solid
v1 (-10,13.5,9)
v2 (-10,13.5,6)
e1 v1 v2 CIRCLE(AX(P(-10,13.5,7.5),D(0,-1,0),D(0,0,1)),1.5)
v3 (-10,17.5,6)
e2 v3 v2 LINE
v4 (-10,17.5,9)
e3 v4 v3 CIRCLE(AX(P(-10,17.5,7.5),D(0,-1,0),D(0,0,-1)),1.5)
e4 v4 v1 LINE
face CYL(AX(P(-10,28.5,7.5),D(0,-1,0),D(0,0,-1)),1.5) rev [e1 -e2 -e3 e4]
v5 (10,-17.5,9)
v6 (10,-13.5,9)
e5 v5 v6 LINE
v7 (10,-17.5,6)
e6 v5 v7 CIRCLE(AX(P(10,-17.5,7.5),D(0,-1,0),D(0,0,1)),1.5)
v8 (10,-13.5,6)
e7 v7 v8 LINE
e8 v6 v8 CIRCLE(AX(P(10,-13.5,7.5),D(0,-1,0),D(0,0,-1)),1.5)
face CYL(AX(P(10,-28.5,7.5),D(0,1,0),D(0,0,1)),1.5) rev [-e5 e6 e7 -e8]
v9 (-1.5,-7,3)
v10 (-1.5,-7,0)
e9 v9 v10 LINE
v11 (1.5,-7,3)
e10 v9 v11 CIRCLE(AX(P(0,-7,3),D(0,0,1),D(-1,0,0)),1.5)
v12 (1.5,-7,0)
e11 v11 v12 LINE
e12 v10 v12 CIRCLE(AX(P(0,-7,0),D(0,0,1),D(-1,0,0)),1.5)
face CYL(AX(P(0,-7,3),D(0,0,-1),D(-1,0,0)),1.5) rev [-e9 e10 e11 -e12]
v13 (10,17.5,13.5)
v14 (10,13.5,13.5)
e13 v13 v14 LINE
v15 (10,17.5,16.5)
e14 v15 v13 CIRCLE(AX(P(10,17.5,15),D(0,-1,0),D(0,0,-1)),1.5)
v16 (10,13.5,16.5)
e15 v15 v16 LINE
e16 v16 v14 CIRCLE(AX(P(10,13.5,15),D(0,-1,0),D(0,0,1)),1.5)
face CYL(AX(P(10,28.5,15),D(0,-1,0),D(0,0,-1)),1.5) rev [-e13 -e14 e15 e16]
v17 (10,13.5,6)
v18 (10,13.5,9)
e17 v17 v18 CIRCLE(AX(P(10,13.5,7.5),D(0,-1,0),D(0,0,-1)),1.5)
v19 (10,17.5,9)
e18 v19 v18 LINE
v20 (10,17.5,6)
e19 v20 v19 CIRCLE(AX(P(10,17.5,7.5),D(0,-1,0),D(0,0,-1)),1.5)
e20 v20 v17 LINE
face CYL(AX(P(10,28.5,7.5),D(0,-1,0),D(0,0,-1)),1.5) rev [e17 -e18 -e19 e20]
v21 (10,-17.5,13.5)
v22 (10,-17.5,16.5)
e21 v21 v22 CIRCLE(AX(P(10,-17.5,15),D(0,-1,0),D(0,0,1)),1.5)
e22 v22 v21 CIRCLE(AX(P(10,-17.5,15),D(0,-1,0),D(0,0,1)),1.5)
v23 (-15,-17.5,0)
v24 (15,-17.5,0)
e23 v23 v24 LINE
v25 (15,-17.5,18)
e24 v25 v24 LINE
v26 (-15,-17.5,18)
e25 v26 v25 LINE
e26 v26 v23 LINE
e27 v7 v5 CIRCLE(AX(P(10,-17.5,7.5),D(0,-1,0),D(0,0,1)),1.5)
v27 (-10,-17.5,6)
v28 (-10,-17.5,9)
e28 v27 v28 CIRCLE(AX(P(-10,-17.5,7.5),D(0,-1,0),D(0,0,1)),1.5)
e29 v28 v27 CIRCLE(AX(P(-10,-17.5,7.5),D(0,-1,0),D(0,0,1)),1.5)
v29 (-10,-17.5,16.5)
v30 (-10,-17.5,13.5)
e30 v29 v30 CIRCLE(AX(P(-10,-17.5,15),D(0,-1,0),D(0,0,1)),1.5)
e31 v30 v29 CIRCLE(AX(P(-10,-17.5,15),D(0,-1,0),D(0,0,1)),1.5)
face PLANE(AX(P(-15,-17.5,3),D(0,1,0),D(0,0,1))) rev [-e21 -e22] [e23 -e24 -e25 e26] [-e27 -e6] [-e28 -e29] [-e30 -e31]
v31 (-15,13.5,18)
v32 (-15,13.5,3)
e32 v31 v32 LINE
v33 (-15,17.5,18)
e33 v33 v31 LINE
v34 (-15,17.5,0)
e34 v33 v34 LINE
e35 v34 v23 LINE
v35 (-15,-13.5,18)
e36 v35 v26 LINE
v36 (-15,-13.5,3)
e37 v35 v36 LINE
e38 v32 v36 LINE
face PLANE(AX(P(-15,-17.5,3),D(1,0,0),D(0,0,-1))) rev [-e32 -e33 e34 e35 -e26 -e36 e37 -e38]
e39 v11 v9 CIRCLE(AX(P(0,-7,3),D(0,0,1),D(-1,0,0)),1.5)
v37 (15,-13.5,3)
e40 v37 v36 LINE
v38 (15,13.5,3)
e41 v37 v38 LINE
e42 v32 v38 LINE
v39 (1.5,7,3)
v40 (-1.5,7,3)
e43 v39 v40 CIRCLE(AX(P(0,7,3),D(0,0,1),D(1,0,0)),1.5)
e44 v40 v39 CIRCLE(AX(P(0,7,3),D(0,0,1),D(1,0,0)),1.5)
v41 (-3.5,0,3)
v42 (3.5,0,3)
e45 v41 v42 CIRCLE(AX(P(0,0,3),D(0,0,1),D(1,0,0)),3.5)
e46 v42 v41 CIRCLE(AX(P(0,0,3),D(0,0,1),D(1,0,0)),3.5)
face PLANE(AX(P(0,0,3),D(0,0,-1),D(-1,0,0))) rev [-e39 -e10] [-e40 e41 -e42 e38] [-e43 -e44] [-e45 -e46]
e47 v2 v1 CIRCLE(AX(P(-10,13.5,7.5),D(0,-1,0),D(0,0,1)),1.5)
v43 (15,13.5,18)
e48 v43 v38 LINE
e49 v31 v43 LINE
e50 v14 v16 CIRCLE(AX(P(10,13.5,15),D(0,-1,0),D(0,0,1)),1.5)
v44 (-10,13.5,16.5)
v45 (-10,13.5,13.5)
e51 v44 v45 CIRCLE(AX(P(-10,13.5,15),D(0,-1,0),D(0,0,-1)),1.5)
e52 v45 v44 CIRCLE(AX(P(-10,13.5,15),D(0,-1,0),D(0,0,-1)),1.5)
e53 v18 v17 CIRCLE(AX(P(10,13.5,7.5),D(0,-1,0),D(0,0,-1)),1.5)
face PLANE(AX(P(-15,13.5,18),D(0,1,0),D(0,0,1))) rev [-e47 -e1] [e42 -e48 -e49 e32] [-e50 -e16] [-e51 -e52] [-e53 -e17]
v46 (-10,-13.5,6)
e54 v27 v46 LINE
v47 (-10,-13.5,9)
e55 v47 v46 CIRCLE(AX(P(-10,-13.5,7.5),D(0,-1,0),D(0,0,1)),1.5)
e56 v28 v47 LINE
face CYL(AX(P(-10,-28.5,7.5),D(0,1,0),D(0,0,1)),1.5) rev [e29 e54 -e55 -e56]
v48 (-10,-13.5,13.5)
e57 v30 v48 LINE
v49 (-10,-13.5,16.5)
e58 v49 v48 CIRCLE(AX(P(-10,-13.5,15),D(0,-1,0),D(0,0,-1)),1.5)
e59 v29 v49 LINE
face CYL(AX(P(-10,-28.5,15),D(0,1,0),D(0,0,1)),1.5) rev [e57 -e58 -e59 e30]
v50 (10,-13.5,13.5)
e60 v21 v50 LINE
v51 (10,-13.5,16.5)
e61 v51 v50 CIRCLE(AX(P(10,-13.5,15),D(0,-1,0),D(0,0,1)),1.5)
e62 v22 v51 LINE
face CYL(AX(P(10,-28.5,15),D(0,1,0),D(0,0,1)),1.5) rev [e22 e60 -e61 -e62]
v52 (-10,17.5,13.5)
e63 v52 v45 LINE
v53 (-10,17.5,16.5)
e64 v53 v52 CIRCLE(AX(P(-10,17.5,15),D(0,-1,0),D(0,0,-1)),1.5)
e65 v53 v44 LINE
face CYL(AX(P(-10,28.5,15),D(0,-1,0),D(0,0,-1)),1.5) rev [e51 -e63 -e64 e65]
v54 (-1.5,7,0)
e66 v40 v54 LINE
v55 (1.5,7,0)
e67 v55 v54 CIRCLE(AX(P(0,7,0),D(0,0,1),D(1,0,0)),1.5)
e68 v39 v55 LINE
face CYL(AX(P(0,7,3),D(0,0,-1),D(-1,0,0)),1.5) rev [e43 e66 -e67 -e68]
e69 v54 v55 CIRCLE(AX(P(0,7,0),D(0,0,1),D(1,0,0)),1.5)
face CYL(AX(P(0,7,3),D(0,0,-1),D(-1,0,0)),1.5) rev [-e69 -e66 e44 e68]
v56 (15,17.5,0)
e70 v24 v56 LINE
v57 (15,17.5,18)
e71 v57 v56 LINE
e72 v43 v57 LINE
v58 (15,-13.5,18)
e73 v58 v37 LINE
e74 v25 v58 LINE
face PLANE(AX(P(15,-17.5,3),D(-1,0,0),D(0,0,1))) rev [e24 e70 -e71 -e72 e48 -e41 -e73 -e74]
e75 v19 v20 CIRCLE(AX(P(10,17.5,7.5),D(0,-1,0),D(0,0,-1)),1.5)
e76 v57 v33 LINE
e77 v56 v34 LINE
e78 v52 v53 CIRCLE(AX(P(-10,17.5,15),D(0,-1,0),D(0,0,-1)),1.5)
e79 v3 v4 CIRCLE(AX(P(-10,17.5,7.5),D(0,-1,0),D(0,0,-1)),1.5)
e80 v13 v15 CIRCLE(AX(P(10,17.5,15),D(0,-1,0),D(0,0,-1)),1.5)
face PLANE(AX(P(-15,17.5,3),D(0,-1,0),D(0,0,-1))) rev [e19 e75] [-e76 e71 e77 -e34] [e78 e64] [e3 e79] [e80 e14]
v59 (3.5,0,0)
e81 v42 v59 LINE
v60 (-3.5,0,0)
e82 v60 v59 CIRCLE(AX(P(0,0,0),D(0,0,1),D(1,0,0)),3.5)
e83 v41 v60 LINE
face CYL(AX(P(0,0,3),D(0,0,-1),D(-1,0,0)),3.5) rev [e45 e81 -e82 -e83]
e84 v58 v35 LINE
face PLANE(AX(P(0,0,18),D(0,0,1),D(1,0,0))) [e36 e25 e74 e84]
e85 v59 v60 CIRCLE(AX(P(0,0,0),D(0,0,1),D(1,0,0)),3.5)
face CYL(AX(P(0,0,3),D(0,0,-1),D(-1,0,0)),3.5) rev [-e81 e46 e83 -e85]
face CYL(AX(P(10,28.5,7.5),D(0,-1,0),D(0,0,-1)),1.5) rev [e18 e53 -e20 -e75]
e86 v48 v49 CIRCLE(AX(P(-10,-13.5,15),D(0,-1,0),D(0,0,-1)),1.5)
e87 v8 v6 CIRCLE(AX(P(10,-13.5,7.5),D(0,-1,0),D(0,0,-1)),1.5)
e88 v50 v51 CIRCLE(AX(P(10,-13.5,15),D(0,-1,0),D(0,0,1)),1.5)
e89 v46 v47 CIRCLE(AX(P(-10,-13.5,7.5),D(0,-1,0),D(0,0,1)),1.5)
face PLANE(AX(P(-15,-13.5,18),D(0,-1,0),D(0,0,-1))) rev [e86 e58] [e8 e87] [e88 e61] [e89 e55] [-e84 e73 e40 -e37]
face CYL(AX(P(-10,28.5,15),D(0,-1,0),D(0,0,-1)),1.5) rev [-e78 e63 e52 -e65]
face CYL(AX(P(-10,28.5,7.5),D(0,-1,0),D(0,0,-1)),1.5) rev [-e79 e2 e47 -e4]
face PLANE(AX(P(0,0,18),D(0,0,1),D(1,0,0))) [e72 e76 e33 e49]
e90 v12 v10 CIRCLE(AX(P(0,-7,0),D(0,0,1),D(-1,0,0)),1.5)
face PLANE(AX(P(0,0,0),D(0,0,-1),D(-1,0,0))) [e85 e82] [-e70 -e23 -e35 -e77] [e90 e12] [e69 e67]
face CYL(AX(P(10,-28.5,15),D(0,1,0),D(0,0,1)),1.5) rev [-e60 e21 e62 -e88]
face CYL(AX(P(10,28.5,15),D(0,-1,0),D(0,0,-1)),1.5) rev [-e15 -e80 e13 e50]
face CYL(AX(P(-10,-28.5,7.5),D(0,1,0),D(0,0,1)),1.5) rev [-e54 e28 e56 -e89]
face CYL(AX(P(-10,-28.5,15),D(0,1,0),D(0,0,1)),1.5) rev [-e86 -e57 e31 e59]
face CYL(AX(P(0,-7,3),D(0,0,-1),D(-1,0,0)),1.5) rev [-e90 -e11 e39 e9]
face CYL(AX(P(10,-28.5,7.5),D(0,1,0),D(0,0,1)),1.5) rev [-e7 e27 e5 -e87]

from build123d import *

# Parameters (mm, degrees)
SKETCH1_W           = 30
SKETCH1_H           = 35
SKETCH1_R           = 3.5
SKETCH1_R_2         = 1.5
BOSS_EXTRUDE1_DEPTH = 3
SKETCH2_W           = 30
SKETCH2_H           = 4
BOSS_EXTRUDE2_DEPTH = 15
SKETCH4_R           = 1.5
CUT_EXTRUDE1_DEPTH  = 15


with BuildPart() as part:
    # Sketch1 → Boss-Extrude1 (new body)
    with BuildSketch(Plane.XY):
        Rectangle(SKETCH1_W, SKETCH1_H)
        Circle(SKETCH1_R, mode=Mode.SUBTRACT)
        with Locations((0, 7)):
            Circle(SKETCH1_R_2, mode=Mode.SUBTRACT)
        with Locations(Location((0, -7, 0), (0, 0, 180))):
            Circle(SKETCH1_R_2, mode=Mode.SUBTRACT)
    extrude(amount=BOSS_EXTRUDE1_DEPTH)

    # Sketch2 → Boss-Extrude2 (add)
    with BuildSketch(Plane.XY.offset(3)):
        with Locations((0, 15.5)):
            Rectangle(SKETCH2_W, SKETCH2_H)
        with Locations((0, -15.5)):
            Rectangle(SKETCH2_W, SKETCH2_H)
    extrude(amount=BOSS_EXTRUDE2_DEPTH)

    # Sketch4 → Cut-Extrude1 (cut)
    with BuildSketch(Plane.XZ.offset(-13.5)):
        with Locations(Location((-10, 15, 0), (0, 0, 270))):
            Circle(SKETCH4_R)
        with Locations(Location((10, 15, 0), (0, 0, 270))):
            Circle(SKETCH4_R)
        with Locations(Location((10, 7.5, 0), (0, 0, 270))):
            Circle(SKETCH4_R)
        with Locations(Location((-10, 7.5, 0), (0, 0, 270))):
            Circle(SKETCH4_R)
    cut_extrude1 = extrude(amount=-CUT_EXTRUDE1_DEPTH, mode=Mode.SUBTRACT)

    # Mirror1: Cut-Extrude1 across plane
    add(cut_extrude1.mirror(Plane.ZX), mode=Mode.SUBTRACT)


solid = part.part
